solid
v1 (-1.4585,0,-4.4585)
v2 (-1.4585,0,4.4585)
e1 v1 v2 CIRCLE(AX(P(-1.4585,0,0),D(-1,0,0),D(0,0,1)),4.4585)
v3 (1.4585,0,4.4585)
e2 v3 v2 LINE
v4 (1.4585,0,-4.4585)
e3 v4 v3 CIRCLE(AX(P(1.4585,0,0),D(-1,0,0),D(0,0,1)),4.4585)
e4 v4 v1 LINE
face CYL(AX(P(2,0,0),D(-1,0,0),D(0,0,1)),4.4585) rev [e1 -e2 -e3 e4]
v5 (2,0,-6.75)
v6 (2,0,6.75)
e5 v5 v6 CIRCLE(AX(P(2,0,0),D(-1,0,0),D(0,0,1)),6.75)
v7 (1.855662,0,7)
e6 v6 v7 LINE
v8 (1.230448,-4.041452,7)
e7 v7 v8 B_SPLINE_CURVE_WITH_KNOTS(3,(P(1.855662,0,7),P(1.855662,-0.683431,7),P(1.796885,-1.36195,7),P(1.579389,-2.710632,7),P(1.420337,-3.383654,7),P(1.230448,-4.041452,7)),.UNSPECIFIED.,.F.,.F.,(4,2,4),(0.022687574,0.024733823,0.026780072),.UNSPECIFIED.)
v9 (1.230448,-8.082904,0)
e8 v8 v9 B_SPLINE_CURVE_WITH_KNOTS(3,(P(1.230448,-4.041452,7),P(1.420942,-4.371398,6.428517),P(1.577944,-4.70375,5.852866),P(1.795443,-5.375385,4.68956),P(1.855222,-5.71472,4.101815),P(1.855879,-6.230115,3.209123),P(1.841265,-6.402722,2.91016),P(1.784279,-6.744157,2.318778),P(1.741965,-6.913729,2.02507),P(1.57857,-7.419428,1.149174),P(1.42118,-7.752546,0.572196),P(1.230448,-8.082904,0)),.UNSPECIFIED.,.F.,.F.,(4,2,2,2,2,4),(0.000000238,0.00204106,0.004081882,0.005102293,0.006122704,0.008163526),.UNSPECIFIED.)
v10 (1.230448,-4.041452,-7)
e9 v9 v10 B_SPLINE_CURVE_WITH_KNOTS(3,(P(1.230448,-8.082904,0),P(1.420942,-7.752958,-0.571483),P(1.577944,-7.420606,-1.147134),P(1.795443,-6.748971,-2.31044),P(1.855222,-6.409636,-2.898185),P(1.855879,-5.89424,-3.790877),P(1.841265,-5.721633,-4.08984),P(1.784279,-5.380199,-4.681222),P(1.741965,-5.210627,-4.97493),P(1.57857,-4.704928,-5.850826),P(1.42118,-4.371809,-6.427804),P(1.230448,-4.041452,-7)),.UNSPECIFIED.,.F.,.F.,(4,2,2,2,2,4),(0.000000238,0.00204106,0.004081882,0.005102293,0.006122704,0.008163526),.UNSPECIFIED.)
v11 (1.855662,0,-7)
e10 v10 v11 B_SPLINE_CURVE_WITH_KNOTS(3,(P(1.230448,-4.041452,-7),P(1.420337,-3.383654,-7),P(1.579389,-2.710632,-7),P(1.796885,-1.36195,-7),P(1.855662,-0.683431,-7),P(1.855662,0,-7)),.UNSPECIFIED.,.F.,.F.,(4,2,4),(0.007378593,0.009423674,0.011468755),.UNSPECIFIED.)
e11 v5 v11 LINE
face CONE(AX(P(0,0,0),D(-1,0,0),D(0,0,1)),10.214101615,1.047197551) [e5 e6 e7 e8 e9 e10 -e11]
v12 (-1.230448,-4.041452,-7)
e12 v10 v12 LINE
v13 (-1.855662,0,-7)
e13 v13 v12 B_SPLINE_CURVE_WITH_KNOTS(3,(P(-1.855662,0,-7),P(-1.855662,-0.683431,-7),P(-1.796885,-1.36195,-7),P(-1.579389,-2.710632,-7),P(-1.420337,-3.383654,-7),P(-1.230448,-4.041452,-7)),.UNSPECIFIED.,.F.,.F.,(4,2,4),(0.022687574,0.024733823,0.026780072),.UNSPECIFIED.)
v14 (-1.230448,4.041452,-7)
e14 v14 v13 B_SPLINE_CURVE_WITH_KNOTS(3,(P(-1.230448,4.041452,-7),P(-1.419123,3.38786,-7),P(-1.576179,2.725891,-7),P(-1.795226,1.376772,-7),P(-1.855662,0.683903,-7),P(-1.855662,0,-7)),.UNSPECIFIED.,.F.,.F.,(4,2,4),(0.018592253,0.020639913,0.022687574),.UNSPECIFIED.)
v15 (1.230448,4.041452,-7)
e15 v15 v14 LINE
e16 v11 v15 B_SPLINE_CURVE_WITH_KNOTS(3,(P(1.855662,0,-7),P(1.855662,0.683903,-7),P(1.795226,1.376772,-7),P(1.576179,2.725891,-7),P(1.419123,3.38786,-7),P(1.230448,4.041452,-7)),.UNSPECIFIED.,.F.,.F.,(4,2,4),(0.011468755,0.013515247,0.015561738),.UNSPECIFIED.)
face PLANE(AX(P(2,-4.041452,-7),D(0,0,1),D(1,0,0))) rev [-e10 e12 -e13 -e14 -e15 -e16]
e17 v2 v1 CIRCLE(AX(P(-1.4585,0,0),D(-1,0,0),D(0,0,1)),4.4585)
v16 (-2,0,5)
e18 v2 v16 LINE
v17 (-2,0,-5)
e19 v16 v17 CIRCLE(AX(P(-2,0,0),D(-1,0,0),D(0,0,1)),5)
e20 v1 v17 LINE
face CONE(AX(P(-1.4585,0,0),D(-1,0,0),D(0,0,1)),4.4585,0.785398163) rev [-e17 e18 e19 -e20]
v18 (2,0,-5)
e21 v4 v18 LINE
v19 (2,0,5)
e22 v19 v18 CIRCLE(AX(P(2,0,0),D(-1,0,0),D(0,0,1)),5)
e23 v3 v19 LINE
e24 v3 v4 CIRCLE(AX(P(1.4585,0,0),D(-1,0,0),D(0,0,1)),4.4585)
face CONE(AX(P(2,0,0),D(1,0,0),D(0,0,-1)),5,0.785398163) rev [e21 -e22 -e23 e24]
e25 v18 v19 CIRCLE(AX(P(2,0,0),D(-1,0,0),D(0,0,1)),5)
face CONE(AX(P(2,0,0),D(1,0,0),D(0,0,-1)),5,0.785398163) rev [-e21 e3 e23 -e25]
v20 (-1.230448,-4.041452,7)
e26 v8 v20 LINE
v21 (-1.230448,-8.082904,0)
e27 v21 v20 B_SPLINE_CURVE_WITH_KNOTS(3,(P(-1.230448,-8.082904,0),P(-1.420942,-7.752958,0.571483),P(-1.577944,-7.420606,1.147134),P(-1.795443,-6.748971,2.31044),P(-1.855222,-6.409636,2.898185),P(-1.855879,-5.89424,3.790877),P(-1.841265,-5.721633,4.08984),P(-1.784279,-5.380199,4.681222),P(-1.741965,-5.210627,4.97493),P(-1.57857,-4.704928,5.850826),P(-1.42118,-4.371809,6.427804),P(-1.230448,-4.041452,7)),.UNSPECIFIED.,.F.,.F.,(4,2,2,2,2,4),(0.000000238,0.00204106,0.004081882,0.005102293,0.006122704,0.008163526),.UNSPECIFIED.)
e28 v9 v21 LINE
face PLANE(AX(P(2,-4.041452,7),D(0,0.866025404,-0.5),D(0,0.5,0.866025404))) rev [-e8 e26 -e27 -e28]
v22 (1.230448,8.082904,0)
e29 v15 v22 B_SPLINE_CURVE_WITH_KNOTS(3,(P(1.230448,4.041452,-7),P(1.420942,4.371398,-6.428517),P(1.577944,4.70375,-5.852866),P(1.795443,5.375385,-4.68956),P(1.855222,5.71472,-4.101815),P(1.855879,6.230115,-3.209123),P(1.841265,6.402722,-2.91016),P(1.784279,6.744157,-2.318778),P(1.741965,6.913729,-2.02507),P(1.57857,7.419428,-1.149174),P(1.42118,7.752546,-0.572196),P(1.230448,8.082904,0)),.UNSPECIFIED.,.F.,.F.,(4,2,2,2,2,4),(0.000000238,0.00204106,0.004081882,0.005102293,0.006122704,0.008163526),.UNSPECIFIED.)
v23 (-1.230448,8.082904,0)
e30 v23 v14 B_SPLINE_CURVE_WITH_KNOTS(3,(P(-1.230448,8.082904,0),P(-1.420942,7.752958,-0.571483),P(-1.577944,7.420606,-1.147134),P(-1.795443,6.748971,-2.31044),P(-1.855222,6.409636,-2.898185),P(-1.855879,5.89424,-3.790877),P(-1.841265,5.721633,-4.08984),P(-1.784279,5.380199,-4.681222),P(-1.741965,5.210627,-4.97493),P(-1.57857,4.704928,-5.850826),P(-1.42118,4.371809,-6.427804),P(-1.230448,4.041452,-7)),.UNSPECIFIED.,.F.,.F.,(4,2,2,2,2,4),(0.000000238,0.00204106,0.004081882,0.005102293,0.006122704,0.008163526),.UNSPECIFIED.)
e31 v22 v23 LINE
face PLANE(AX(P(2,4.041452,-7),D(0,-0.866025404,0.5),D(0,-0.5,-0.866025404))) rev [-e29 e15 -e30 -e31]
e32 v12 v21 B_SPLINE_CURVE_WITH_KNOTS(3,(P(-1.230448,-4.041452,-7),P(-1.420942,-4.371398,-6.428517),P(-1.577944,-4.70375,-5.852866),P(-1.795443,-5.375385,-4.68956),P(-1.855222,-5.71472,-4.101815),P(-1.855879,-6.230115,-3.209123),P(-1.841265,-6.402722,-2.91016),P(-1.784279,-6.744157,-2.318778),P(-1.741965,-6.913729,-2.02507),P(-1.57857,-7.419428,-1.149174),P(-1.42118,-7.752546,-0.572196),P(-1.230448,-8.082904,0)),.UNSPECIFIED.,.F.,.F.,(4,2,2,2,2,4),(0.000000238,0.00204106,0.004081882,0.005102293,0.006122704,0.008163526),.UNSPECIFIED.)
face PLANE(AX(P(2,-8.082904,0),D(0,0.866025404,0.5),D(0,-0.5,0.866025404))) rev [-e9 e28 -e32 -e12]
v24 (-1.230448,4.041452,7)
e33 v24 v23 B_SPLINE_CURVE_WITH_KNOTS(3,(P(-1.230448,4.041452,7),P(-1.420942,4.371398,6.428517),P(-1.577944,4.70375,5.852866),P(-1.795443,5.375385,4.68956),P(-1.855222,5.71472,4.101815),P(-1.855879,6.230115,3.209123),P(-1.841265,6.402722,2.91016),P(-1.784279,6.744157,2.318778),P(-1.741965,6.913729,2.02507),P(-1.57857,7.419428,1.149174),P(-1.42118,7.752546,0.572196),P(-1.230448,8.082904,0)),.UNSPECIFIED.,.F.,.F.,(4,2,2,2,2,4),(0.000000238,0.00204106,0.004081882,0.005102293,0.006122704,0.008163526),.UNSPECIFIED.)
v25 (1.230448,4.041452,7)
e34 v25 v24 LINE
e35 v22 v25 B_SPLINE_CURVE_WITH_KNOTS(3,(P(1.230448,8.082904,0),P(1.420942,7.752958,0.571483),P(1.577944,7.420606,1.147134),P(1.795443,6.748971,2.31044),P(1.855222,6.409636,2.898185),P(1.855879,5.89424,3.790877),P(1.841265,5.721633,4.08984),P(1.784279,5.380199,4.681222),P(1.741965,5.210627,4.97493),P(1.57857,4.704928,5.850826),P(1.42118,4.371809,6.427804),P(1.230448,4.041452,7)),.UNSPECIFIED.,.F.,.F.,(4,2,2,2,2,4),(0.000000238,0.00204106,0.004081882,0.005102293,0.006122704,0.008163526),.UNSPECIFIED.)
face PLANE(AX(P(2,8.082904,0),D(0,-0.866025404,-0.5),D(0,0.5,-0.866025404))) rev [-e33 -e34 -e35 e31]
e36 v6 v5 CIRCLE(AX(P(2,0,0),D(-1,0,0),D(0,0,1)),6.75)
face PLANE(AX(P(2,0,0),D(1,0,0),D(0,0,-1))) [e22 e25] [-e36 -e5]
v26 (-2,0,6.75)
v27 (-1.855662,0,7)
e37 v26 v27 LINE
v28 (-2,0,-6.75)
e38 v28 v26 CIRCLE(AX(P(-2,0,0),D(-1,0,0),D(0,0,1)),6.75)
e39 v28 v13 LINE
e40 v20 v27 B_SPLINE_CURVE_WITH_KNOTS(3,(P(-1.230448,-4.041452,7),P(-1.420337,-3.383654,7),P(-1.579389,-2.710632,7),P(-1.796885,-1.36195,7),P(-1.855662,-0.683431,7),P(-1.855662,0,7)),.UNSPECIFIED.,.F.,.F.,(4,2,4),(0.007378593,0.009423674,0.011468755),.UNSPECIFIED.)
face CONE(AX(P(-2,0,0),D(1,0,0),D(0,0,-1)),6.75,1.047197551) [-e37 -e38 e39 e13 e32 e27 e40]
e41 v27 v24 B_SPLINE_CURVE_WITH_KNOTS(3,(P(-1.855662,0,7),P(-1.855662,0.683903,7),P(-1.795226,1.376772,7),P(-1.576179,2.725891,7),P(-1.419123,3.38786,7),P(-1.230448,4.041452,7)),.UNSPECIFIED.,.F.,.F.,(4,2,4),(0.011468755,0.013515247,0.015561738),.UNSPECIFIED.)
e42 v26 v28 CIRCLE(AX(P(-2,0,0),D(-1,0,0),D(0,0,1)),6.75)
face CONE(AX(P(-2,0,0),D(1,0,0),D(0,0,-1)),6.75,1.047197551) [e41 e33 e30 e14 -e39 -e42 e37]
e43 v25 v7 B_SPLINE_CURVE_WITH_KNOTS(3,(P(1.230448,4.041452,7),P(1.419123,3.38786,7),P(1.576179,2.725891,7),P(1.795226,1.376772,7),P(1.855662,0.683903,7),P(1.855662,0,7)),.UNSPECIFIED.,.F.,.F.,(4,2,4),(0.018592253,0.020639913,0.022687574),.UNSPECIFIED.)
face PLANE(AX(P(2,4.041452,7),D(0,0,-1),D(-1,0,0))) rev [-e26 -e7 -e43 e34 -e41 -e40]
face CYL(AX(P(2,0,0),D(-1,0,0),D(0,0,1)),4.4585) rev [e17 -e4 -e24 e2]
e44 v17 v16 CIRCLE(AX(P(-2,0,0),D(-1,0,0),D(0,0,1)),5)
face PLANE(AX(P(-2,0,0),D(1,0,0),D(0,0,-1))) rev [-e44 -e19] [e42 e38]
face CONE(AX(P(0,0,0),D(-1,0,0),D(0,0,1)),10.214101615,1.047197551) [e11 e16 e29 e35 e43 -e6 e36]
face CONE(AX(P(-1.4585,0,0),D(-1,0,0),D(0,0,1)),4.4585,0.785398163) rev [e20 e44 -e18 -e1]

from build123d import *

# Parameters (mm, degrees)
EXTRUDE_1_DEPTH      = 2
EXTRUDE_1_DEPTH_BACK = 2


with BuildPart() as part:
    # 草图1 → 凸台-拉伸1 (new, two sides: drawn at the far end of the back side and taken through both)
    with BuildSketch(Plane(origin=(0, 0, 0), x_dir=(0, 0, -1), z_dir=(1, 0, 0)).offset(-EXTRUDE_1_DEPTH_BACK)):
        Polygon((-7, 4.041451884), (-7, -4.041451884), (0, -8.082903769), (7, -4.041451884), (7, 4.041451884), (0, 8.082903769), align=None)
    extrude(amount=EXTRUDE_1_DEPTH + EXTRUDE_1_DEPTH_BACK)

    # 草图2 → 切除-旋转1 (revolve, cut)
    with BuildSketch(Plane.XY, mode=Mode.PRIVATE) as cut_revolve_1_sk:
        Polygon((-2, 0), (-2, 5), (-1.4585, 4.4585), (1.4585, 4.4585), (2, 5), (2, 0), align=None)
    revolve(cut_revolve_1_sk.sketch.rotate(Axis((2, 0, 0), (-1, 0, 0)), 270), axis=Axis((2, 0, 0), (-1, 0, 0)), mode=Mode.SUBTRACT)

    # 草图3 → 切除-旋转2 (revolve, cut)
    with BuildSketch(Plane.XY, mode=Mode.PRIVATE) as cut_revolve_2_sk:
        Polygon((-7, 16.75), (-7, 1), (-2, 1), (-2, 6.75), (0, 10.214101615), (2, 6.75), (2, 1), (7, 1), (7, 16.75), align=None)
    revolve(cut_revolve_2_sk.sketch.rotate(Axis((50, 0, 0), (-1, 0, 0)), 270), axis=Axis((50, 0, 0), (-1, 0, 0)), mode=Mode.SUBTRACT)


solid = part.part
